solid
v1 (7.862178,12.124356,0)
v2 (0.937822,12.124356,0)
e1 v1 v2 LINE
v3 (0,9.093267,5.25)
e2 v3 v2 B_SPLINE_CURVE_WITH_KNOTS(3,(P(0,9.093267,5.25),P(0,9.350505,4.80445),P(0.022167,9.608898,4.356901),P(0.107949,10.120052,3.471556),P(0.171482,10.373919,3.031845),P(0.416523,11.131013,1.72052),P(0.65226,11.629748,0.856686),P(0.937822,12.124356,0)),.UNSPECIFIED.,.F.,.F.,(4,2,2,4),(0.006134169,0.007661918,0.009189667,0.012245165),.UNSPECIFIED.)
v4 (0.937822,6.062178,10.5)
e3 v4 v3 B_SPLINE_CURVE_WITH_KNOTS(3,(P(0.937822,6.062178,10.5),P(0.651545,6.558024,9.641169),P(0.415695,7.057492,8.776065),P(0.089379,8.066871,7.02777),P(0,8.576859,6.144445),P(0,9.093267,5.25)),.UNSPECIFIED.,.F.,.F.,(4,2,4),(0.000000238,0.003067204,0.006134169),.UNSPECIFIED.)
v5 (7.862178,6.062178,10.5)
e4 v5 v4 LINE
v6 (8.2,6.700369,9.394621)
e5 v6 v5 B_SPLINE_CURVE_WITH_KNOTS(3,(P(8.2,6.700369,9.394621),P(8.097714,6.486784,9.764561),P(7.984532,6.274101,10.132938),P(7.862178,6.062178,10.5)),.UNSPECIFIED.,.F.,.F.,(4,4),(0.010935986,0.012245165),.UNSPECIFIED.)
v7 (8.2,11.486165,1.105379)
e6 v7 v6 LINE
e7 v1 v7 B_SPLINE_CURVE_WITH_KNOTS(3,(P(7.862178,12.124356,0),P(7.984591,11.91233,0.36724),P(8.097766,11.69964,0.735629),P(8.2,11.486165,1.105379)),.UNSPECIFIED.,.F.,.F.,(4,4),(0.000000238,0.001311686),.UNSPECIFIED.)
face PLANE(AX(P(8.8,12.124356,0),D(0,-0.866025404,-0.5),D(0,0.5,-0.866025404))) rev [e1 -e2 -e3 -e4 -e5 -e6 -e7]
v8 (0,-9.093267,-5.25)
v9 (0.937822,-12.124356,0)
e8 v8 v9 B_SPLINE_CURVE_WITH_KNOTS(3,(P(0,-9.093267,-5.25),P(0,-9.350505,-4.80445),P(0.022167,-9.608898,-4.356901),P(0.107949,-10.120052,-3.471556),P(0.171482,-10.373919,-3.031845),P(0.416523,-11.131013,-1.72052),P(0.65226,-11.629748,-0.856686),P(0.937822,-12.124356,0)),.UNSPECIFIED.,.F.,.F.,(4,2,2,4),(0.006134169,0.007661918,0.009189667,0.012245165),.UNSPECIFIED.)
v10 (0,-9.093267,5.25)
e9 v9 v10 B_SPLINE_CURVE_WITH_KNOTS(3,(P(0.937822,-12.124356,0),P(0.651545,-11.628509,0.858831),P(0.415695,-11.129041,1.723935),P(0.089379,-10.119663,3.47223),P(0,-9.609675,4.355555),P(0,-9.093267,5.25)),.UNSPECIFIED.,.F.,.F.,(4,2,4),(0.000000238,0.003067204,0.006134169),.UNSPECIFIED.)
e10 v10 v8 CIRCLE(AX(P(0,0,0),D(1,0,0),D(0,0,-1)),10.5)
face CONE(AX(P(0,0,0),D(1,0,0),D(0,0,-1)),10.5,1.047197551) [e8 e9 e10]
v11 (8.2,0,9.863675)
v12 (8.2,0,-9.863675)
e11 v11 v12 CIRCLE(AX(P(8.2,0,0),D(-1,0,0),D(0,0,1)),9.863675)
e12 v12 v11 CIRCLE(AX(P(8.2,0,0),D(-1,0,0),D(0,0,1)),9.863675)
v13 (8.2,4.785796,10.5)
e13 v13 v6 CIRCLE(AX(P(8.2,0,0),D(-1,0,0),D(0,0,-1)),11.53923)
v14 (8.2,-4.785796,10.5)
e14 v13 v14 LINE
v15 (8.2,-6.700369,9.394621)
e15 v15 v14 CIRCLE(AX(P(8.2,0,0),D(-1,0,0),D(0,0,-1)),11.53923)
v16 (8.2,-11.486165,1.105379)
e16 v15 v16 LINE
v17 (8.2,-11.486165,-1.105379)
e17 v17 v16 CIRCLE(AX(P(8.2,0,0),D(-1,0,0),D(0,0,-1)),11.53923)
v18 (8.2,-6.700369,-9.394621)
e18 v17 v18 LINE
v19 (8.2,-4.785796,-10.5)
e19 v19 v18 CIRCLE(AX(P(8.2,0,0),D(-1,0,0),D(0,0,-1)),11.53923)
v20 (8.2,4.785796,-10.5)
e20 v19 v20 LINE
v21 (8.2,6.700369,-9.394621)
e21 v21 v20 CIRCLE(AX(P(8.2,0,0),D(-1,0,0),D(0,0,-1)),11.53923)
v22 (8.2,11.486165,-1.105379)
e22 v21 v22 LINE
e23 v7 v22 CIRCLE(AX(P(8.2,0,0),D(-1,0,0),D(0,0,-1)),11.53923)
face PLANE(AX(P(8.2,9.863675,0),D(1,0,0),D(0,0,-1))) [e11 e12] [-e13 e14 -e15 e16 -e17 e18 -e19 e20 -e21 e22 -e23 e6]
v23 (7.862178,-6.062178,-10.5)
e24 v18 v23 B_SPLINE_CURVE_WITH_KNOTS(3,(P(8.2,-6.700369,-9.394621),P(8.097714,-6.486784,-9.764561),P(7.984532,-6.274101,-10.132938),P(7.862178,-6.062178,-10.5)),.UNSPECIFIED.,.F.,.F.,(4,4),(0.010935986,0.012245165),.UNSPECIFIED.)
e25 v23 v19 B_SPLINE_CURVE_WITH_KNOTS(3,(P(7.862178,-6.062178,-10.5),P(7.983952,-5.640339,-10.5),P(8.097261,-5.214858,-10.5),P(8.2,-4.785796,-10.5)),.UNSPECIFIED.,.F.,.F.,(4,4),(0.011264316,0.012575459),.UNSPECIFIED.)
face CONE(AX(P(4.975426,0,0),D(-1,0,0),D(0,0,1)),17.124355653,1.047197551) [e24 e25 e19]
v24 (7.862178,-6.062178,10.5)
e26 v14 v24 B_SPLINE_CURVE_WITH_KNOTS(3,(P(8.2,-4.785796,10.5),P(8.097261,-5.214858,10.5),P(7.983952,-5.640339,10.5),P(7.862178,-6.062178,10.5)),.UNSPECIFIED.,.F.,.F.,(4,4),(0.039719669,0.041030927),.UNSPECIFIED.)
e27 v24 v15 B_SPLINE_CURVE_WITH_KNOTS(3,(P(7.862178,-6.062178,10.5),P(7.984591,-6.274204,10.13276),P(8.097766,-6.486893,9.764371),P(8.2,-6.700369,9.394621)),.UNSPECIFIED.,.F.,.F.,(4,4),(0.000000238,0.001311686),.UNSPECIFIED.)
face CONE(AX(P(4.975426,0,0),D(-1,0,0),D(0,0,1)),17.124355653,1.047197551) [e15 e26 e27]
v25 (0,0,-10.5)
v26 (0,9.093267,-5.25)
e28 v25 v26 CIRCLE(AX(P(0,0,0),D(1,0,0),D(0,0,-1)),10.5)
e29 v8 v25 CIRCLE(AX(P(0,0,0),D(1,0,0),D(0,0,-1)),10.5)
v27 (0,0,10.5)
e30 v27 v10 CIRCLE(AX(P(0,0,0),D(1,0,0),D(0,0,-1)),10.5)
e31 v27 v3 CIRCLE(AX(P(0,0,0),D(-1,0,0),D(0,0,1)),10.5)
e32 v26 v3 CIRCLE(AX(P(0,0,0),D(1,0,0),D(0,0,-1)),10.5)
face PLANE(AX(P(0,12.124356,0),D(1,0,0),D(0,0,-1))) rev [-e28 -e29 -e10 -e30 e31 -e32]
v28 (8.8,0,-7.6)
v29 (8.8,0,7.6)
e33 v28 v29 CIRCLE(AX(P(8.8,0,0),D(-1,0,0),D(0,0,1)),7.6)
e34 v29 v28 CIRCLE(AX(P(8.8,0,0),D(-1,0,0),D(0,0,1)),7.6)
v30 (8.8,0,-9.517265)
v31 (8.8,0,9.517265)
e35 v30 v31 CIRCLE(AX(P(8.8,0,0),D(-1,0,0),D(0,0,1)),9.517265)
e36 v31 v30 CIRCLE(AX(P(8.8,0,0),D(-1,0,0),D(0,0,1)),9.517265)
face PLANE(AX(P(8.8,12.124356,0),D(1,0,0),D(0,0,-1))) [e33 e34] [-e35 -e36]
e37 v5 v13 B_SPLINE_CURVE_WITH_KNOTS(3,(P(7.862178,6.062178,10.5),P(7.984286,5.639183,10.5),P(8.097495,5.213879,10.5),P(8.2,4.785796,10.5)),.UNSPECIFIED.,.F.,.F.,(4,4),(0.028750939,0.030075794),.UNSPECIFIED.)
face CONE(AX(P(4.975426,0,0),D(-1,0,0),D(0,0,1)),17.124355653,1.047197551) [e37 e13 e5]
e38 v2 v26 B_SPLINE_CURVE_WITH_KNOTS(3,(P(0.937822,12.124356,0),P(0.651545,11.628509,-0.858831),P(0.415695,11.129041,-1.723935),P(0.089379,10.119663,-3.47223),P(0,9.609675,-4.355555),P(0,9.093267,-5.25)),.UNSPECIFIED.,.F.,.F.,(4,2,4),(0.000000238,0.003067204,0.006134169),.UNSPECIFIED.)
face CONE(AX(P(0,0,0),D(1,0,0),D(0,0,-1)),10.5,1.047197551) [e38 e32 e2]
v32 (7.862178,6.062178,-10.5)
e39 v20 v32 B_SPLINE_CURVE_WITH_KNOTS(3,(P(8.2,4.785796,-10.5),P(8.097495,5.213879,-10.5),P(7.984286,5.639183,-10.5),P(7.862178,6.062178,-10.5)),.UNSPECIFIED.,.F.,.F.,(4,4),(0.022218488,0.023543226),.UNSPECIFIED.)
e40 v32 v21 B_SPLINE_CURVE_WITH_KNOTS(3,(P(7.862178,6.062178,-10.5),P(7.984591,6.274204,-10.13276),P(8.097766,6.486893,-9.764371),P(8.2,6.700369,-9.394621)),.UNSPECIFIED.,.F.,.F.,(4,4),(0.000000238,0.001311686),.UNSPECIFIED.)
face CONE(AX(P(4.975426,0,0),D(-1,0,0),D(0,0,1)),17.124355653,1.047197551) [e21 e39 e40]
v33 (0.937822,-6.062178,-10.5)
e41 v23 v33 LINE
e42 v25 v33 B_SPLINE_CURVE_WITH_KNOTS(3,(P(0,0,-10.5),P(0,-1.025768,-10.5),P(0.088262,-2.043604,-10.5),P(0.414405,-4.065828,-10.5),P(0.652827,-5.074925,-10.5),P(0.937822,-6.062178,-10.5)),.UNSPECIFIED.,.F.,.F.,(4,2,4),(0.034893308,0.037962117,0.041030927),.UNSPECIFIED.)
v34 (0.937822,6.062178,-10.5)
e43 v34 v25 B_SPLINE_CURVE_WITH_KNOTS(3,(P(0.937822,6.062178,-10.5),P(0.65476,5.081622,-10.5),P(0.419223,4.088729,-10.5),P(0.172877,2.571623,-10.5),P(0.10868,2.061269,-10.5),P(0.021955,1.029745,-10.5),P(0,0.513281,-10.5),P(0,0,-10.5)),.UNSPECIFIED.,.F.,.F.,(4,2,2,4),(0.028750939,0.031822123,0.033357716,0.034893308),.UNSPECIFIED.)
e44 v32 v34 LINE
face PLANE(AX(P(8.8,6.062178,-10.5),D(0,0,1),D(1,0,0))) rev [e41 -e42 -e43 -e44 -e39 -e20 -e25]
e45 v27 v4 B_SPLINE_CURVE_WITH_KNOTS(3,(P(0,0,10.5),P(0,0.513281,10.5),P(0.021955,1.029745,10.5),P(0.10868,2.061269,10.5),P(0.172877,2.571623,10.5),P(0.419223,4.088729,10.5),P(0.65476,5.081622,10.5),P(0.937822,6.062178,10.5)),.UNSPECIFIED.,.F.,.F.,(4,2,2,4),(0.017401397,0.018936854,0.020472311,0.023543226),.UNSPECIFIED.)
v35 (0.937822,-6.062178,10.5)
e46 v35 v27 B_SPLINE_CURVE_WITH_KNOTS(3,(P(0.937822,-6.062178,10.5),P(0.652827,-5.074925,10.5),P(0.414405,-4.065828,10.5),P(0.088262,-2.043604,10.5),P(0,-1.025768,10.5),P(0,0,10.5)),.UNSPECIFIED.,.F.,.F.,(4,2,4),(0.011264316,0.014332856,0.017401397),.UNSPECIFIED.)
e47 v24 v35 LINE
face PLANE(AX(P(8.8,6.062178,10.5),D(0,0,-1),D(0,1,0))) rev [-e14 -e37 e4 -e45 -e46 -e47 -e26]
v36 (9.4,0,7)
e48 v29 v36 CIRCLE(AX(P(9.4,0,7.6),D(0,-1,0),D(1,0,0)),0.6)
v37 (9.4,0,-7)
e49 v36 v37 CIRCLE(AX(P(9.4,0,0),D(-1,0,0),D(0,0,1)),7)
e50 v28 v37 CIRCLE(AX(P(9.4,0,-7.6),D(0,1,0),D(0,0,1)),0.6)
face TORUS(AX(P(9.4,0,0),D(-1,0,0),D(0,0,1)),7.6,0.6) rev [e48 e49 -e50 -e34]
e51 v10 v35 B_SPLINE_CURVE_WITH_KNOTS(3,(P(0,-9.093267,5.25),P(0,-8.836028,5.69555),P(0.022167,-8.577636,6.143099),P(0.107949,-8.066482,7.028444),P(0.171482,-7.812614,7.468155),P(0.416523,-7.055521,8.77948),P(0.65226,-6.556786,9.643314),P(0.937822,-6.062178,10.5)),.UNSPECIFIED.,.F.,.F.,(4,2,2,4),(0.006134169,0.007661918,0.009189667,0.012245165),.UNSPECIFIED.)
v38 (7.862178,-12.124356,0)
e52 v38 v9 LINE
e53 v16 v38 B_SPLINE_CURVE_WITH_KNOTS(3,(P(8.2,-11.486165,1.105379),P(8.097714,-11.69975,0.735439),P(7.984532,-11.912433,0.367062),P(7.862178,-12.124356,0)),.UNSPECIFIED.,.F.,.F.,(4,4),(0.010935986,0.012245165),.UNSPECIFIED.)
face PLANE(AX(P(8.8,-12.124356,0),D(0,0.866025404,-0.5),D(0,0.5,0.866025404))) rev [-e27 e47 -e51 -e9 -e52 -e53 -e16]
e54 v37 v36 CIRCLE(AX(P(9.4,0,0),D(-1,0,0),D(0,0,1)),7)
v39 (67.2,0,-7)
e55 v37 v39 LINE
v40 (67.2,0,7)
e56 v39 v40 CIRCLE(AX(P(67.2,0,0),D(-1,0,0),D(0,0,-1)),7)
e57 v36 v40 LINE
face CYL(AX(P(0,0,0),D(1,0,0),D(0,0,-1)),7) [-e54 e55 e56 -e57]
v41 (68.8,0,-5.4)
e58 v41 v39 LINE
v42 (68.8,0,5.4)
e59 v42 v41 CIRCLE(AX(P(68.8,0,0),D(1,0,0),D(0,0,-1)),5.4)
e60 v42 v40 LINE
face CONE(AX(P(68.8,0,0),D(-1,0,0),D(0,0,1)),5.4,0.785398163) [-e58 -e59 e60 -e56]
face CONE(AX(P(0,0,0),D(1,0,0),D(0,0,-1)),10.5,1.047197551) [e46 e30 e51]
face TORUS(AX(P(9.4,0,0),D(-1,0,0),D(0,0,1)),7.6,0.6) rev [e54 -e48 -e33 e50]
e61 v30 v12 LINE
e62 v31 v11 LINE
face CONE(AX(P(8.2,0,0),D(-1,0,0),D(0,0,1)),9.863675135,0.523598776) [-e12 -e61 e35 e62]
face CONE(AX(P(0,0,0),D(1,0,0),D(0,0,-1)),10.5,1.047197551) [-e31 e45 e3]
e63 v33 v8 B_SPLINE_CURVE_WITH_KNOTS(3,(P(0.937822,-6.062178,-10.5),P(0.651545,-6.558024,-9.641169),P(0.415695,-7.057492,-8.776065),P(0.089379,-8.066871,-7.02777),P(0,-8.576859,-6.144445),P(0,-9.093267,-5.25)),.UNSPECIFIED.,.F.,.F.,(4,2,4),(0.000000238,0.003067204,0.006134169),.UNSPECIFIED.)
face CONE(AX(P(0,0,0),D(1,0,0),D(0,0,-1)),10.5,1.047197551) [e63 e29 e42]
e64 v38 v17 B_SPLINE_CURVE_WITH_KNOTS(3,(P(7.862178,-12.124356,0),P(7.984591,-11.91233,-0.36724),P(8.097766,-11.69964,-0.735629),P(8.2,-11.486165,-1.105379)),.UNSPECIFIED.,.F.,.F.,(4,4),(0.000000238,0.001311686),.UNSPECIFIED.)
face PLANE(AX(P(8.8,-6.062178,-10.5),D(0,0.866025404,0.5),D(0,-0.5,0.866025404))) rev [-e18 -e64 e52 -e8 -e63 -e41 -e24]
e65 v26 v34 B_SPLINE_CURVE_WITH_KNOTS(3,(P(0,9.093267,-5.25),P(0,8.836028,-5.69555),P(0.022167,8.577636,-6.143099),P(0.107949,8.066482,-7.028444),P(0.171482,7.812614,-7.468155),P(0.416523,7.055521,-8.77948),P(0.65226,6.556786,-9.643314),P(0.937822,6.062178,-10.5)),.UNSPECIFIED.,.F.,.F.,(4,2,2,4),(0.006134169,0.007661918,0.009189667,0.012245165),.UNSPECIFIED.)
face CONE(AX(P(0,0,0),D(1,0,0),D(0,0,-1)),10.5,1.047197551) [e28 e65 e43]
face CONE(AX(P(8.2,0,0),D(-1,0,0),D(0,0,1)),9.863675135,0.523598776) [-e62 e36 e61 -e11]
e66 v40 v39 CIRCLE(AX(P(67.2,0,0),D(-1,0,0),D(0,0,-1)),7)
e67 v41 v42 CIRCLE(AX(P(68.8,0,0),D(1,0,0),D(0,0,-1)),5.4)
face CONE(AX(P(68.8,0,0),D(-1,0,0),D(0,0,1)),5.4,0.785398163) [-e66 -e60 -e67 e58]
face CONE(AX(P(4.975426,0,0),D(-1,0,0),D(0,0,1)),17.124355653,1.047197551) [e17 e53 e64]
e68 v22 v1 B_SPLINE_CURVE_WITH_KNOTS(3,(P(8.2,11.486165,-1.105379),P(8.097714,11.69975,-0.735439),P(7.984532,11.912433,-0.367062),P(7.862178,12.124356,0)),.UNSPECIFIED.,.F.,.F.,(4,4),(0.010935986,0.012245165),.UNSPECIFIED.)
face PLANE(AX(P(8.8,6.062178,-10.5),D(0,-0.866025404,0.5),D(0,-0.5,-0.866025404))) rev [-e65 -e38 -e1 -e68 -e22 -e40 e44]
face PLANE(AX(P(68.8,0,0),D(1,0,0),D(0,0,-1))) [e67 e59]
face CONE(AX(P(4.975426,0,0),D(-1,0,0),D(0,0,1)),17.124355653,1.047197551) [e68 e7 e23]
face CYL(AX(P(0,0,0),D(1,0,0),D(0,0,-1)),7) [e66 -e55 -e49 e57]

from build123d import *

# Parameters (mm, degrees)
BOSS_EXTRUDE_DEPTH = 8.8
CHAMFER_2_SIZE     = 1.6


with BuildPart() as part:
    # Sketch1 → Boss-Extrude (new body)
    with BuildSketch(Plane(origin=(0, 0, 0), x_dir=(0, 0, -1), z_dir=(1, 0, 0))):
        Polygon((10.5, 6.062177826), (10.5, -6.062177826), (0, -12.124355653), (-10.5, -6.062177826), (-10.5, 6.062177826), (0, 12.124355653), align=None)
    extrude(amount=BOSS_EXTRUDE_DEPTH)

    # Sketch2 → Boss-Revolve1 (revolve)
    with BuildSketch(Plane.XY, mode=Mode.PRIVATE) as boss_revolve1_sk:
        Polygon((0, 0), (68.8, 0), (68.8, 5.268), (68.8, 7), (8.8, 7), (0, 7), align=None)
    revolve(boss_revolve1_sk.sketch.rotate(Axis((0, 0, 0), (-1, 0, 0)), 90), axis=Axis((0, 0, 0), (-1, 0, 0)))

    # Sketch3 → Cut-Revolve1 (revolve, cut)
    with BuildSketch(Plane.XY):
        Polygon((0, 10.5), (3.824573519, 17.124355653), (3.824573519, 22.124355653), (-10, 22.124355653), (-10, 10.5), align=None)
    revolve(axis=Axis((0, 0, 0), (1, 0, 0)), mode=Mode.SUBTRACT)

    # Sketch5 → Cut-Revolve2 (revolve, cut)
    with BuildSketch(Plane.XY):
        Polygon((8.8, 10.5), (4.975426481, 17.124355653), (4.975426481, 22.124355653), (14.975426481, 22.124355653), (14.975426481, 10.5), align=None)
    revolve(axis=Axis((0, 0, 0), (1, 0, 0)), mode=Mode.SUBTRACT)

    # Sketch4 → Cut-Revolve3 (revolve, cut)
    with BuildSketch(Plane.XY, mode=Mode.PRIVATE) as cut_revolve3_sk:
        Polygon((8.8, 9.517264973), (8.2, 9.863675135), (8.2, 22.124355653), (8.8, 22.124355653), align=None)
    revolve(cut_revolve3_sk.sketch.rotate(Axis((0, 0, 0), (1, 0, 0)), 90), axis=Axis((0, 0, 0), (1, 0, 0)), mode=Mode.SUBTRACT)

    # Chamfer 2
    chamfer_2_edges = [part.edges().sort_by_distance(p)[0] for p in [
        (68.8, 0, 7),
    ]]
    chamfer(chamfer_2_edges, length=CHAMFER_2_SIZE)

    # Sketch9 → Revolve1 (revolve)
    with BuildSketch(Plane.XY, mode=Mode.PRIVATE) as revolve1_sk:
        with BuildLine():
            Line((8.8, 7.6), (8.8, 7))
            Line((8.8, 7), (9.4, 7))
            ThreePointArc((9.4, 7), (8.975735931, 7.175735931), (8.8, 7.6))
        make_face()
    revolve(revolve1_sk.sketch.rotate(Axis((0, 0, 0), (1, 0, 0)), 90), axis=Axis((0, 0, 0), (1, 0, 0)))


solid = part.part
